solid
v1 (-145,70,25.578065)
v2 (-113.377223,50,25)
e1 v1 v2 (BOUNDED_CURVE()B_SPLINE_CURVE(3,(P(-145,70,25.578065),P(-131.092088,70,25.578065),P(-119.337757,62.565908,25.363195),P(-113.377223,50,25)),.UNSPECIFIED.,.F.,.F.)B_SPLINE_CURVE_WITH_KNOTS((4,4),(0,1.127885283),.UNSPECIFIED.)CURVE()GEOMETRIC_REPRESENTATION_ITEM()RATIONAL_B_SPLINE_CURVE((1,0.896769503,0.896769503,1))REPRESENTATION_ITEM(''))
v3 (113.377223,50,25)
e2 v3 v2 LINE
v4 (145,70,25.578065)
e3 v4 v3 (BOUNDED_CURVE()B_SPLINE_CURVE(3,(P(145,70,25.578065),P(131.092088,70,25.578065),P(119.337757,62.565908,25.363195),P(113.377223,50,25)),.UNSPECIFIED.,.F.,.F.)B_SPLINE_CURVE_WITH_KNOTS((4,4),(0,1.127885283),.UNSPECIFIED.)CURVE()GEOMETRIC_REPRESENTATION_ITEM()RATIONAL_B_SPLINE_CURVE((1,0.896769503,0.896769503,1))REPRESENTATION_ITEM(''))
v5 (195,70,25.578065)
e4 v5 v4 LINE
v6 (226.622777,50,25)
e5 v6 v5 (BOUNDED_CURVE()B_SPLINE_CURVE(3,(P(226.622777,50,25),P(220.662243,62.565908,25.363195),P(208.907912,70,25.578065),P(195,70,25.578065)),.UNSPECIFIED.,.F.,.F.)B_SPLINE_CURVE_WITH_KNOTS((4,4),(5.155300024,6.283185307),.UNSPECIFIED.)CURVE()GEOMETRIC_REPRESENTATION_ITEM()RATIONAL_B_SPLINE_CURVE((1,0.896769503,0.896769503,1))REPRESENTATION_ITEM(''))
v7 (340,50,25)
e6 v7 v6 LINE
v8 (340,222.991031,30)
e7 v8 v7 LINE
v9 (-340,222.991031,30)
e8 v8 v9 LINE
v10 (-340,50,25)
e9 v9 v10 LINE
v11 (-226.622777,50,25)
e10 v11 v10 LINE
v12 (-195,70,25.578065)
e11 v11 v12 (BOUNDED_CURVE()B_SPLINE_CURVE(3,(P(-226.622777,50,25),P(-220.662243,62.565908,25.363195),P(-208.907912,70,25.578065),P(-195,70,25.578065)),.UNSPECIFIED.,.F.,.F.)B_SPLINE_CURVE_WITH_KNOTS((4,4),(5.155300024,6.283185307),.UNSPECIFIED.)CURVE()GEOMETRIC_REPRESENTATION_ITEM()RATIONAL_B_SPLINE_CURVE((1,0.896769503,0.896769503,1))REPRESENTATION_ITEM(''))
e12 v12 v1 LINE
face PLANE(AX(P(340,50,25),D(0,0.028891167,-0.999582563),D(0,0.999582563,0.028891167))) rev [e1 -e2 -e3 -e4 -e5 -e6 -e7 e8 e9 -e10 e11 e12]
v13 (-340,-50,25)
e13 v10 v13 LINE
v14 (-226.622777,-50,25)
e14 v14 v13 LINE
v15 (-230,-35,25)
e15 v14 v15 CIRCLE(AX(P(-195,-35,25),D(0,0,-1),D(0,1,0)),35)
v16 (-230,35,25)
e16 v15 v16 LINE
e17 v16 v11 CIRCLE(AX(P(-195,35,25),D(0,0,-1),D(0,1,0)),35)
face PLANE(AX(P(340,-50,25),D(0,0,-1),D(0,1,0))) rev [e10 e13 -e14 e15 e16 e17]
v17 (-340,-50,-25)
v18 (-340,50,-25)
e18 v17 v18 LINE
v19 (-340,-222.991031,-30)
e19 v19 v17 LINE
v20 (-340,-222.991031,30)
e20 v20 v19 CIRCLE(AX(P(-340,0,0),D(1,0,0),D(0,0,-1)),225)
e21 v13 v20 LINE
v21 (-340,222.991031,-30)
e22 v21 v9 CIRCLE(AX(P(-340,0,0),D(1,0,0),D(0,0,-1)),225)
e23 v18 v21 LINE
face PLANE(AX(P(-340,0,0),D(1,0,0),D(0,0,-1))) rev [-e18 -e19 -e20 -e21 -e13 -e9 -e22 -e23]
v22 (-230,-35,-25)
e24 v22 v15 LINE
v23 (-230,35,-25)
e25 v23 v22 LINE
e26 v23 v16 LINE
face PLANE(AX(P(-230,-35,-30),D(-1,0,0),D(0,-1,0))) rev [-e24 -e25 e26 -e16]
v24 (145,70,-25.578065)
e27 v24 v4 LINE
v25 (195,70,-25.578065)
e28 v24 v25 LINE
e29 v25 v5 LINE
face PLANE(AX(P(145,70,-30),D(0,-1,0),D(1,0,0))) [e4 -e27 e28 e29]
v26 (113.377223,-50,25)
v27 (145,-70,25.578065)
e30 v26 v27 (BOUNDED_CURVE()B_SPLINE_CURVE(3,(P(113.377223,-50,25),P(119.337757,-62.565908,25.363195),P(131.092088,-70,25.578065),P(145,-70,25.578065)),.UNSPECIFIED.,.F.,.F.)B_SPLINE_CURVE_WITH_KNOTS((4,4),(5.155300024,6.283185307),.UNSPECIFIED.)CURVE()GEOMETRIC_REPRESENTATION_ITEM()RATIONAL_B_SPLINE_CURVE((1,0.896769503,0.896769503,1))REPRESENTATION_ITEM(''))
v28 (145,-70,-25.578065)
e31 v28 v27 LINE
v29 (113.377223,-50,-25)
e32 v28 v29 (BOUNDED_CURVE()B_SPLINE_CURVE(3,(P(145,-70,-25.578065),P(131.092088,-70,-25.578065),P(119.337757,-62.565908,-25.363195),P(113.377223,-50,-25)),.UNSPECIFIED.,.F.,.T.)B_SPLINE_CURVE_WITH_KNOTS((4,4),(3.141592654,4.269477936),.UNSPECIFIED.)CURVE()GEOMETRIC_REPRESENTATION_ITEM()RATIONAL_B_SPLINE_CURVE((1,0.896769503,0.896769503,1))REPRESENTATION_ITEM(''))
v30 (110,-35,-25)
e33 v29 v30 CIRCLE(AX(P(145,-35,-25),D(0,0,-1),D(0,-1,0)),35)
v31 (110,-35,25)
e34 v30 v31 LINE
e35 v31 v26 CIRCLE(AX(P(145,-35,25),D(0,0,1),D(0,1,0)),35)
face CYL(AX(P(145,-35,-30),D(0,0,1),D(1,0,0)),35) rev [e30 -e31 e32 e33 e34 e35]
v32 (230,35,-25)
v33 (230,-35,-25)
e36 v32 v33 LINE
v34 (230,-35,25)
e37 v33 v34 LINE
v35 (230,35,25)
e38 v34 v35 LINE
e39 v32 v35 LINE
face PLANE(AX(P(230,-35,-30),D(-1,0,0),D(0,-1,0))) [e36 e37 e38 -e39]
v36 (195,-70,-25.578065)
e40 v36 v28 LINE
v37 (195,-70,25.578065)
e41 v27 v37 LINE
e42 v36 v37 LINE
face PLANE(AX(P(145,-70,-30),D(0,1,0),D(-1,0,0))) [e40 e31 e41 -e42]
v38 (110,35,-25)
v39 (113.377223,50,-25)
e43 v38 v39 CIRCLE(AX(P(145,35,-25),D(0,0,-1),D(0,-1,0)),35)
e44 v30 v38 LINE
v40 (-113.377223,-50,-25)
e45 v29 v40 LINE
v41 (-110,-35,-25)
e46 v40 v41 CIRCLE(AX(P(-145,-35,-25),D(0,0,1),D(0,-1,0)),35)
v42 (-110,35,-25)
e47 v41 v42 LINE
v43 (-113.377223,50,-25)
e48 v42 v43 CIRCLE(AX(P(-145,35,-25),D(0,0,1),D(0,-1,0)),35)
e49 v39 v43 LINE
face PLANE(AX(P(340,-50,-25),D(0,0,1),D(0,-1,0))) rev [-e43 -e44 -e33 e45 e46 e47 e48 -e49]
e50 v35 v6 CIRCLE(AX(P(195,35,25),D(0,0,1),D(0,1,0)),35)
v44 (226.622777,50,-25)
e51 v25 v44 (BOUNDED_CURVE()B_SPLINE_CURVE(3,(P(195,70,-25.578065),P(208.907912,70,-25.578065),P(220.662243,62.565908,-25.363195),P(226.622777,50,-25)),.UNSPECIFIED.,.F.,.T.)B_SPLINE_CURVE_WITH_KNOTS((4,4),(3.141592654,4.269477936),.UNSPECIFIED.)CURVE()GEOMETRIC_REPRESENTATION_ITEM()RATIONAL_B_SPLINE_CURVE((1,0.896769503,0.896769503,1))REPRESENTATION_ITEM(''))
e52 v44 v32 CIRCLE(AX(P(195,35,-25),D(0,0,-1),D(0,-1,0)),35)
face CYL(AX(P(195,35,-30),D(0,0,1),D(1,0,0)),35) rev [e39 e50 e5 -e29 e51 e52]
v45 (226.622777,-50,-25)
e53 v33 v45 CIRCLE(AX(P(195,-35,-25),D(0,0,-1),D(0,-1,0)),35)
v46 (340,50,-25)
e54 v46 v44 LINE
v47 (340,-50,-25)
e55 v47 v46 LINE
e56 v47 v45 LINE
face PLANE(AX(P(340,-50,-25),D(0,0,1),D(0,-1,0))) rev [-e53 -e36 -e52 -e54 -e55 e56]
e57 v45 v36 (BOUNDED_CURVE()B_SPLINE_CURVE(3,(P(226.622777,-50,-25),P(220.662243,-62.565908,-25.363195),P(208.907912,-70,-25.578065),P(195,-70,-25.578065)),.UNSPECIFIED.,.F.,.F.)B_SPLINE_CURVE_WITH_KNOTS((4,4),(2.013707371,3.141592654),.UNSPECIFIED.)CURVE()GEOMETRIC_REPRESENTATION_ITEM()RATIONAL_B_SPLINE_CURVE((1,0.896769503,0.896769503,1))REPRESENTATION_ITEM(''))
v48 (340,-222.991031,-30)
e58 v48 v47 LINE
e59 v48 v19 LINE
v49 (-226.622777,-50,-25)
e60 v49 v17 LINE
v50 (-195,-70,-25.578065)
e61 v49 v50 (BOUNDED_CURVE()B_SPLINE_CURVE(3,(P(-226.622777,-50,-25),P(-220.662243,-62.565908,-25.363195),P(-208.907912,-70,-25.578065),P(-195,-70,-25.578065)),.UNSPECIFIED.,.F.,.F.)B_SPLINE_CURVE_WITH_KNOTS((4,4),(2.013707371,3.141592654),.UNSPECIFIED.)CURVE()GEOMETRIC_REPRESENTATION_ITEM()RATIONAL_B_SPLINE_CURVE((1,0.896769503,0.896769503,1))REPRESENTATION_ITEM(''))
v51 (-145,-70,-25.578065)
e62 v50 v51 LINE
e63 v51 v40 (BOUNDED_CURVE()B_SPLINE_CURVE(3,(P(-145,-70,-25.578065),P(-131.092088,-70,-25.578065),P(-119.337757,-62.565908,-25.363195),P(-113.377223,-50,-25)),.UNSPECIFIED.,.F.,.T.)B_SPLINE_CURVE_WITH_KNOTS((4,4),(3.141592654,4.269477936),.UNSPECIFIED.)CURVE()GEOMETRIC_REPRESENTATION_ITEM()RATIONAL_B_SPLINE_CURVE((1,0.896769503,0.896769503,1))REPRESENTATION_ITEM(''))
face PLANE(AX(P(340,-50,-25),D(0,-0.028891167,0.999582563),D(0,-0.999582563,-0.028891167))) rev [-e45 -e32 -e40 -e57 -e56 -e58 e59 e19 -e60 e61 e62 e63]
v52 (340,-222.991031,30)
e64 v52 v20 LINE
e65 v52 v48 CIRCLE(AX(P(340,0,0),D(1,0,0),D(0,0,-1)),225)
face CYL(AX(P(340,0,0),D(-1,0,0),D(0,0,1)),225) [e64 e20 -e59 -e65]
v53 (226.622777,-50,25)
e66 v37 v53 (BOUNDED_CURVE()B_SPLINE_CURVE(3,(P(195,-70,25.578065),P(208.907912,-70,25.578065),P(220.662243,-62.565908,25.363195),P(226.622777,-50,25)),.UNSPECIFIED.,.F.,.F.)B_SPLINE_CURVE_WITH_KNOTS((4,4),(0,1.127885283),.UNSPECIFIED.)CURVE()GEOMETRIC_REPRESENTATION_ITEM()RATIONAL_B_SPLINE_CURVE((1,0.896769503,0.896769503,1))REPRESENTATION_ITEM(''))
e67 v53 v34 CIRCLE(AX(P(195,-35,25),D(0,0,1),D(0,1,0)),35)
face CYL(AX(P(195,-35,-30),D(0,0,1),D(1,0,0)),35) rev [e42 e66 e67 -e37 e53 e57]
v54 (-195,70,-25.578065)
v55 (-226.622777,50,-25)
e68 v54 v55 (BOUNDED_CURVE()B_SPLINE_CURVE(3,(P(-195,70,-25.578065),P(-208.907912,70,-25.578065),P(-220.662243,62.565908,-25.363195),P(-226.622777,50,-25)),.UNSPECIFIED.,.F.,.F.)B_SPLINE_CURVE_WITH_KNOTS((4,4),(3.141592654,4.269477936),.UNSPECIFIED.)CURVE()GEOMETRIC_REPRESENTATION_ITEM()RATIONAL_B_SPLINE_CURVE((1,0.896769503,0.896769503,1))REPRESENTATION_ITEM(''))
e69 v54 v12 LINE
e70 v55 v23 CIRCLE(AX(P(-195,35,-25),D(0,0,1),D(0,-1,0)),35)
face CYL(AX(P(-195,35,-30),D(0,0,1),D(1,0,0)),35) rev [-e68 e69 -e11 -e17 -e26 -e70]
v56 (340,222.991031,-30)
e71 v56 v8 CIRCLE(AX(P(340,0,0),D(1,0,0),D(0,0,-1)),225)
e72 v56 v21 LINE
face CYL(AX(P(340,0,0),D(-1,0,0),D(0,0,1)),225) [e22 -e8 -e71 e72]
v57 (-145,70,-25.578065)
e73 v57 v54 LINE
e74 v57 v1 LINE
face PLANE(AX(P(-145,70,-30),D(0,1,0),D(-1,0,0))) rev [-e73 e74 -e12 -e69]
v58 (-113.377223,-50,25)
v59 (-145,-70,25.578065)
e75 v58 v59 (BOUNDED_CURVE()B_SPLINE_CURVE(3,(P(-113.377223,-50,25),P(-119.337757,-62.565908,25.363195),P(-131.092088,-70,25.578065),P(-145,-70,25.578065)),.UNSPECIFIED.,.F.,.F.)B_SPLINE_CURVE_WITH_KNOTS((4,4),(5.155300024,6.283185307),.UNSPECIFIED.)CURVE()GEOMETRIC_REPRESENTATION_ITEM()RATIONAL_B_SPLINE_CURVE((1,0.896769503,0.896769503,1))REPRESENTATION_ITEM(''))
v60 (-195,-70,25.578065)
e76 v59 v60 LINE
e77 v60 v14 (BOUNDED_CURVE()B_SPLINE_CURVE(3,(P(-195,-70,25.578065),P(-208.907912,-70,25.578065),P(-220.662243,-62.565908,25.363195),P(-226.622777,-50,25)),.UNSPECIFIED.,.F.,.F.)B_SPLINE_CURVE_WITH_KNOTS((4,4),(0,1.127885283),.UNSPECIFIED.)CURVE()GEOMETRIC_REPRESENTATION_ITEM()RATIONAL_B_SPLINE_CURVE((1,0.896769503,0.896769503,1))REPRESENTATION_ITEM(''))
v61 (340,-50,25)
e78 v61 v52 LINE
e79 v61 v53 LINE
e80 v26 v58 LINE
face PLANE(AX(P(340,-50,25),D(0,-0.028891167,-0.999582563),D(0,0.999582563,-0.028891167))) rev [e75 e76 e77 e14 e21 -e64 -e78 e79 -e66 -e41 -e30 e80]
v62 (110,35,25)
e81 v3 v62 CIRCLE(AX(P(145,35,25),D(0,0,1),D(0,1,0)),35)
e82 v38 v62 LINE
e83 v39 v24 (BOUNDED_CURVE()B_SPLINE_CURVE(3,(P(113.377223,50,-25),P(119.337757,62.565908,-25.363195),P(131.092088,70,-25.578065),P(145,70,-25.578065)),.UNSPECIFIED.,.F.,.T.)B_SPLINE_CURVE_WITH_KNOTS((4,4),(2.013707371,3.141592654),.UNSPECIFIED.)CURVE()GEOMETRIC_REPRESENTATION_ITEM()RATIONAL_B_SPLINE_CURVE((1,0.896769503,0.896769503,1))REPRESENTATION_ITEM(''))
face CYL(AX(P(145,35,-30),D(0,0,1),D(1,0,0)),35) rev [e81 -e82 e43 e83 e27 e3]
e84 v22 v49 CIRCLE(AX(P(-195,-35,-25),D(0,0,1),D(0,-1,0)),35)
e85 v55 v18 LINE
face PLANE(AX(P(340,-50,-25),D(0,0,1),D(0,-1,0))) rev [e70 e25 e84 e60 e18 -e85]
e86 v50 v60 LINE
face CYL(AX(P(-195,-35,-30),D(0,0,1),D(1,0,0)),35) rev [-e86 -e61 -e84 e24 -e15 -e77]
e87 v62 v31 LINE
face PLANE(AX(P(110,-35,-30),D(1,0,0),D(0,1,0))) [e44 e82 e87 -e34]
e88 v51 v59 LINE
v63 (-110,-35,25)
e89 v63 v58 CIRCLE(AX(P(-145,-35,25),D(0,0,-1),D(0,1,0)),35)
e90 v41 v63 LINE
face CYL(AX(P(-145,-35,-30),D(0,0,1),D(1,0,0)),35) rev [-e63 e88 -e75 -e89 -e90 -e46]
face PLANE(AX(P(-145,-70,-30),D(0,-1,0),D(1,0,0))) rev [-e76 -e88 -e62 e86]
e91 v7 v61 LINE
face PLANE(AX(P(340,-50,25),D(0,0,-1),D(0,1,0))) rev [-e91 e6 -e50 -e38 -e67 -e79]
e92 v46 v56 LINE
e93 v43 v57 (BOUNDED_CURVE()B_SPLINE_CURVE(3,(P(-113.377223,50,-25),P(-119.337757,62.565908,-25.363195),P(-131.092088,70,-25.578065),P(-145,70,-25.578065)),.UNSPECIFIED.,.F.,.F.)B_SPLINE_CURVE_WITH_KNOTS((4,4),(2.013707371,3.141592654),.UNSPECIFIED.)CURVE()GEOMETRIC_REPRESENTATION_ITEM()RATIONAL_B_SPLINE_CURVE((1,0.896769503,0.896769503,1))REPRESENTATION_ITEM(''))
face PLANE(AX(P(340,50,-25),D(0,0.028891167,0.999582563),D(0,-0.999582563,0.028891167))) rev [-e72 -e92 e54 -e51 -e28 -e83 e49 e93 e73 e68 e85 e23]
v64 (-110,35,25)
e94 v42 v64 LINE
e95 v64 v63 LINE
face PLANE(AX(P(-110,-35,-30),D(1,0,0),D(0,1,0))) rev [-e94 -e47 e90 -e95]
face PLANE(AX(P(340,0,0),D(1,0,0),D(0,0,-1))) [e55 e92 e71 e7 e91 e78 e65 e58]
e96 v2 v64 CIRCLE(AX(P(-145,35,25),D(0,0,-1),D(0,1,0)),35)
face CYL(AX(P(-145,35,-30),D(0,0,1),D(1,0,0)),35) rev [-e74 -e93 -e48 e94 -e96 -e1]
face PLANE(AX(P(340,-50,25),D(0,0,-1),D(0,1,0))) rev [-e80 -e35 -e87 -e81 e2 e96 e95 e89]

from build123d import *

# Parameters (mm, degrees)
BOSS_EXTRUDE1_DEPTH = 340
CUT_EXTRUDE1_DEPTH  = 409.809246471


with BuildPart() as part:
    # Sketch1 → Boss-Extrude1 (new, symmetric)
    with BuildSketch(Plane(origin=(0, 0, 0), x_dir=(0, 0, -1), z_dir=(1, 0, 0))):
        with BuildLine():
            Line((25, -50), (25, 50))
            Line((25, 50), (30, 222.99103121))
            ThreePointArc((30, 222.99103121), (0, 225), (-30, 222.99103121))
            Line((-30, 222.99103121), (-25, 50))
            Line((-25, 50), (-25, -50))
            Line((-25, -50), (-30, -222.99103121))
            ThreePointArc((-30, -222.99103121), (0, -225), (30, -222.99103121))
            Line((30, -222.99103121), (25, -50))
        make_face()
    extrude(amount=BOSS_EXTRUDE1_DEPTH, both=True)

    # Sketch2 → Cut-Extrude1 (cut, symmetric)
    with BuildSketch(Plane.XY):
        with BuildLine():
            Line((-145, -70), (-195, -70))
            ThreePointArc((-195, -70), (-219.748737342, -59.748737342), (-230, -35))
            Line((-230, -35), (-230, 35))
            ThreePointArc((-230, 35), (-219.748737342, 59.748737342), (-195, 70))
            Line((-195, 70), (-145, 70))
            ThreePointArc((-145, 70), (-120.251262658, 59.748737342), (-110, 35))
            Line((-110, 35), (-110, -35))
            ThreePointArc((-110, -35), (-120.251262658, -59.748737342), (-145, -70))
        make_face()
    cut_extrude1 = extrude(amount=CUT_EXTRUDE1_DEPTH, both=True, mode=Mode.SUBTRACT)

    # Mirror1: Cut-Extrude1 across plane
    add(cut_extrude1.mirror(Plane(origin=(0, 0, 0), x_dir=(0, 0, 1), z_dir=(1, 0, 0))), mode=Mode.SUBTRACT)


solid = part.part
